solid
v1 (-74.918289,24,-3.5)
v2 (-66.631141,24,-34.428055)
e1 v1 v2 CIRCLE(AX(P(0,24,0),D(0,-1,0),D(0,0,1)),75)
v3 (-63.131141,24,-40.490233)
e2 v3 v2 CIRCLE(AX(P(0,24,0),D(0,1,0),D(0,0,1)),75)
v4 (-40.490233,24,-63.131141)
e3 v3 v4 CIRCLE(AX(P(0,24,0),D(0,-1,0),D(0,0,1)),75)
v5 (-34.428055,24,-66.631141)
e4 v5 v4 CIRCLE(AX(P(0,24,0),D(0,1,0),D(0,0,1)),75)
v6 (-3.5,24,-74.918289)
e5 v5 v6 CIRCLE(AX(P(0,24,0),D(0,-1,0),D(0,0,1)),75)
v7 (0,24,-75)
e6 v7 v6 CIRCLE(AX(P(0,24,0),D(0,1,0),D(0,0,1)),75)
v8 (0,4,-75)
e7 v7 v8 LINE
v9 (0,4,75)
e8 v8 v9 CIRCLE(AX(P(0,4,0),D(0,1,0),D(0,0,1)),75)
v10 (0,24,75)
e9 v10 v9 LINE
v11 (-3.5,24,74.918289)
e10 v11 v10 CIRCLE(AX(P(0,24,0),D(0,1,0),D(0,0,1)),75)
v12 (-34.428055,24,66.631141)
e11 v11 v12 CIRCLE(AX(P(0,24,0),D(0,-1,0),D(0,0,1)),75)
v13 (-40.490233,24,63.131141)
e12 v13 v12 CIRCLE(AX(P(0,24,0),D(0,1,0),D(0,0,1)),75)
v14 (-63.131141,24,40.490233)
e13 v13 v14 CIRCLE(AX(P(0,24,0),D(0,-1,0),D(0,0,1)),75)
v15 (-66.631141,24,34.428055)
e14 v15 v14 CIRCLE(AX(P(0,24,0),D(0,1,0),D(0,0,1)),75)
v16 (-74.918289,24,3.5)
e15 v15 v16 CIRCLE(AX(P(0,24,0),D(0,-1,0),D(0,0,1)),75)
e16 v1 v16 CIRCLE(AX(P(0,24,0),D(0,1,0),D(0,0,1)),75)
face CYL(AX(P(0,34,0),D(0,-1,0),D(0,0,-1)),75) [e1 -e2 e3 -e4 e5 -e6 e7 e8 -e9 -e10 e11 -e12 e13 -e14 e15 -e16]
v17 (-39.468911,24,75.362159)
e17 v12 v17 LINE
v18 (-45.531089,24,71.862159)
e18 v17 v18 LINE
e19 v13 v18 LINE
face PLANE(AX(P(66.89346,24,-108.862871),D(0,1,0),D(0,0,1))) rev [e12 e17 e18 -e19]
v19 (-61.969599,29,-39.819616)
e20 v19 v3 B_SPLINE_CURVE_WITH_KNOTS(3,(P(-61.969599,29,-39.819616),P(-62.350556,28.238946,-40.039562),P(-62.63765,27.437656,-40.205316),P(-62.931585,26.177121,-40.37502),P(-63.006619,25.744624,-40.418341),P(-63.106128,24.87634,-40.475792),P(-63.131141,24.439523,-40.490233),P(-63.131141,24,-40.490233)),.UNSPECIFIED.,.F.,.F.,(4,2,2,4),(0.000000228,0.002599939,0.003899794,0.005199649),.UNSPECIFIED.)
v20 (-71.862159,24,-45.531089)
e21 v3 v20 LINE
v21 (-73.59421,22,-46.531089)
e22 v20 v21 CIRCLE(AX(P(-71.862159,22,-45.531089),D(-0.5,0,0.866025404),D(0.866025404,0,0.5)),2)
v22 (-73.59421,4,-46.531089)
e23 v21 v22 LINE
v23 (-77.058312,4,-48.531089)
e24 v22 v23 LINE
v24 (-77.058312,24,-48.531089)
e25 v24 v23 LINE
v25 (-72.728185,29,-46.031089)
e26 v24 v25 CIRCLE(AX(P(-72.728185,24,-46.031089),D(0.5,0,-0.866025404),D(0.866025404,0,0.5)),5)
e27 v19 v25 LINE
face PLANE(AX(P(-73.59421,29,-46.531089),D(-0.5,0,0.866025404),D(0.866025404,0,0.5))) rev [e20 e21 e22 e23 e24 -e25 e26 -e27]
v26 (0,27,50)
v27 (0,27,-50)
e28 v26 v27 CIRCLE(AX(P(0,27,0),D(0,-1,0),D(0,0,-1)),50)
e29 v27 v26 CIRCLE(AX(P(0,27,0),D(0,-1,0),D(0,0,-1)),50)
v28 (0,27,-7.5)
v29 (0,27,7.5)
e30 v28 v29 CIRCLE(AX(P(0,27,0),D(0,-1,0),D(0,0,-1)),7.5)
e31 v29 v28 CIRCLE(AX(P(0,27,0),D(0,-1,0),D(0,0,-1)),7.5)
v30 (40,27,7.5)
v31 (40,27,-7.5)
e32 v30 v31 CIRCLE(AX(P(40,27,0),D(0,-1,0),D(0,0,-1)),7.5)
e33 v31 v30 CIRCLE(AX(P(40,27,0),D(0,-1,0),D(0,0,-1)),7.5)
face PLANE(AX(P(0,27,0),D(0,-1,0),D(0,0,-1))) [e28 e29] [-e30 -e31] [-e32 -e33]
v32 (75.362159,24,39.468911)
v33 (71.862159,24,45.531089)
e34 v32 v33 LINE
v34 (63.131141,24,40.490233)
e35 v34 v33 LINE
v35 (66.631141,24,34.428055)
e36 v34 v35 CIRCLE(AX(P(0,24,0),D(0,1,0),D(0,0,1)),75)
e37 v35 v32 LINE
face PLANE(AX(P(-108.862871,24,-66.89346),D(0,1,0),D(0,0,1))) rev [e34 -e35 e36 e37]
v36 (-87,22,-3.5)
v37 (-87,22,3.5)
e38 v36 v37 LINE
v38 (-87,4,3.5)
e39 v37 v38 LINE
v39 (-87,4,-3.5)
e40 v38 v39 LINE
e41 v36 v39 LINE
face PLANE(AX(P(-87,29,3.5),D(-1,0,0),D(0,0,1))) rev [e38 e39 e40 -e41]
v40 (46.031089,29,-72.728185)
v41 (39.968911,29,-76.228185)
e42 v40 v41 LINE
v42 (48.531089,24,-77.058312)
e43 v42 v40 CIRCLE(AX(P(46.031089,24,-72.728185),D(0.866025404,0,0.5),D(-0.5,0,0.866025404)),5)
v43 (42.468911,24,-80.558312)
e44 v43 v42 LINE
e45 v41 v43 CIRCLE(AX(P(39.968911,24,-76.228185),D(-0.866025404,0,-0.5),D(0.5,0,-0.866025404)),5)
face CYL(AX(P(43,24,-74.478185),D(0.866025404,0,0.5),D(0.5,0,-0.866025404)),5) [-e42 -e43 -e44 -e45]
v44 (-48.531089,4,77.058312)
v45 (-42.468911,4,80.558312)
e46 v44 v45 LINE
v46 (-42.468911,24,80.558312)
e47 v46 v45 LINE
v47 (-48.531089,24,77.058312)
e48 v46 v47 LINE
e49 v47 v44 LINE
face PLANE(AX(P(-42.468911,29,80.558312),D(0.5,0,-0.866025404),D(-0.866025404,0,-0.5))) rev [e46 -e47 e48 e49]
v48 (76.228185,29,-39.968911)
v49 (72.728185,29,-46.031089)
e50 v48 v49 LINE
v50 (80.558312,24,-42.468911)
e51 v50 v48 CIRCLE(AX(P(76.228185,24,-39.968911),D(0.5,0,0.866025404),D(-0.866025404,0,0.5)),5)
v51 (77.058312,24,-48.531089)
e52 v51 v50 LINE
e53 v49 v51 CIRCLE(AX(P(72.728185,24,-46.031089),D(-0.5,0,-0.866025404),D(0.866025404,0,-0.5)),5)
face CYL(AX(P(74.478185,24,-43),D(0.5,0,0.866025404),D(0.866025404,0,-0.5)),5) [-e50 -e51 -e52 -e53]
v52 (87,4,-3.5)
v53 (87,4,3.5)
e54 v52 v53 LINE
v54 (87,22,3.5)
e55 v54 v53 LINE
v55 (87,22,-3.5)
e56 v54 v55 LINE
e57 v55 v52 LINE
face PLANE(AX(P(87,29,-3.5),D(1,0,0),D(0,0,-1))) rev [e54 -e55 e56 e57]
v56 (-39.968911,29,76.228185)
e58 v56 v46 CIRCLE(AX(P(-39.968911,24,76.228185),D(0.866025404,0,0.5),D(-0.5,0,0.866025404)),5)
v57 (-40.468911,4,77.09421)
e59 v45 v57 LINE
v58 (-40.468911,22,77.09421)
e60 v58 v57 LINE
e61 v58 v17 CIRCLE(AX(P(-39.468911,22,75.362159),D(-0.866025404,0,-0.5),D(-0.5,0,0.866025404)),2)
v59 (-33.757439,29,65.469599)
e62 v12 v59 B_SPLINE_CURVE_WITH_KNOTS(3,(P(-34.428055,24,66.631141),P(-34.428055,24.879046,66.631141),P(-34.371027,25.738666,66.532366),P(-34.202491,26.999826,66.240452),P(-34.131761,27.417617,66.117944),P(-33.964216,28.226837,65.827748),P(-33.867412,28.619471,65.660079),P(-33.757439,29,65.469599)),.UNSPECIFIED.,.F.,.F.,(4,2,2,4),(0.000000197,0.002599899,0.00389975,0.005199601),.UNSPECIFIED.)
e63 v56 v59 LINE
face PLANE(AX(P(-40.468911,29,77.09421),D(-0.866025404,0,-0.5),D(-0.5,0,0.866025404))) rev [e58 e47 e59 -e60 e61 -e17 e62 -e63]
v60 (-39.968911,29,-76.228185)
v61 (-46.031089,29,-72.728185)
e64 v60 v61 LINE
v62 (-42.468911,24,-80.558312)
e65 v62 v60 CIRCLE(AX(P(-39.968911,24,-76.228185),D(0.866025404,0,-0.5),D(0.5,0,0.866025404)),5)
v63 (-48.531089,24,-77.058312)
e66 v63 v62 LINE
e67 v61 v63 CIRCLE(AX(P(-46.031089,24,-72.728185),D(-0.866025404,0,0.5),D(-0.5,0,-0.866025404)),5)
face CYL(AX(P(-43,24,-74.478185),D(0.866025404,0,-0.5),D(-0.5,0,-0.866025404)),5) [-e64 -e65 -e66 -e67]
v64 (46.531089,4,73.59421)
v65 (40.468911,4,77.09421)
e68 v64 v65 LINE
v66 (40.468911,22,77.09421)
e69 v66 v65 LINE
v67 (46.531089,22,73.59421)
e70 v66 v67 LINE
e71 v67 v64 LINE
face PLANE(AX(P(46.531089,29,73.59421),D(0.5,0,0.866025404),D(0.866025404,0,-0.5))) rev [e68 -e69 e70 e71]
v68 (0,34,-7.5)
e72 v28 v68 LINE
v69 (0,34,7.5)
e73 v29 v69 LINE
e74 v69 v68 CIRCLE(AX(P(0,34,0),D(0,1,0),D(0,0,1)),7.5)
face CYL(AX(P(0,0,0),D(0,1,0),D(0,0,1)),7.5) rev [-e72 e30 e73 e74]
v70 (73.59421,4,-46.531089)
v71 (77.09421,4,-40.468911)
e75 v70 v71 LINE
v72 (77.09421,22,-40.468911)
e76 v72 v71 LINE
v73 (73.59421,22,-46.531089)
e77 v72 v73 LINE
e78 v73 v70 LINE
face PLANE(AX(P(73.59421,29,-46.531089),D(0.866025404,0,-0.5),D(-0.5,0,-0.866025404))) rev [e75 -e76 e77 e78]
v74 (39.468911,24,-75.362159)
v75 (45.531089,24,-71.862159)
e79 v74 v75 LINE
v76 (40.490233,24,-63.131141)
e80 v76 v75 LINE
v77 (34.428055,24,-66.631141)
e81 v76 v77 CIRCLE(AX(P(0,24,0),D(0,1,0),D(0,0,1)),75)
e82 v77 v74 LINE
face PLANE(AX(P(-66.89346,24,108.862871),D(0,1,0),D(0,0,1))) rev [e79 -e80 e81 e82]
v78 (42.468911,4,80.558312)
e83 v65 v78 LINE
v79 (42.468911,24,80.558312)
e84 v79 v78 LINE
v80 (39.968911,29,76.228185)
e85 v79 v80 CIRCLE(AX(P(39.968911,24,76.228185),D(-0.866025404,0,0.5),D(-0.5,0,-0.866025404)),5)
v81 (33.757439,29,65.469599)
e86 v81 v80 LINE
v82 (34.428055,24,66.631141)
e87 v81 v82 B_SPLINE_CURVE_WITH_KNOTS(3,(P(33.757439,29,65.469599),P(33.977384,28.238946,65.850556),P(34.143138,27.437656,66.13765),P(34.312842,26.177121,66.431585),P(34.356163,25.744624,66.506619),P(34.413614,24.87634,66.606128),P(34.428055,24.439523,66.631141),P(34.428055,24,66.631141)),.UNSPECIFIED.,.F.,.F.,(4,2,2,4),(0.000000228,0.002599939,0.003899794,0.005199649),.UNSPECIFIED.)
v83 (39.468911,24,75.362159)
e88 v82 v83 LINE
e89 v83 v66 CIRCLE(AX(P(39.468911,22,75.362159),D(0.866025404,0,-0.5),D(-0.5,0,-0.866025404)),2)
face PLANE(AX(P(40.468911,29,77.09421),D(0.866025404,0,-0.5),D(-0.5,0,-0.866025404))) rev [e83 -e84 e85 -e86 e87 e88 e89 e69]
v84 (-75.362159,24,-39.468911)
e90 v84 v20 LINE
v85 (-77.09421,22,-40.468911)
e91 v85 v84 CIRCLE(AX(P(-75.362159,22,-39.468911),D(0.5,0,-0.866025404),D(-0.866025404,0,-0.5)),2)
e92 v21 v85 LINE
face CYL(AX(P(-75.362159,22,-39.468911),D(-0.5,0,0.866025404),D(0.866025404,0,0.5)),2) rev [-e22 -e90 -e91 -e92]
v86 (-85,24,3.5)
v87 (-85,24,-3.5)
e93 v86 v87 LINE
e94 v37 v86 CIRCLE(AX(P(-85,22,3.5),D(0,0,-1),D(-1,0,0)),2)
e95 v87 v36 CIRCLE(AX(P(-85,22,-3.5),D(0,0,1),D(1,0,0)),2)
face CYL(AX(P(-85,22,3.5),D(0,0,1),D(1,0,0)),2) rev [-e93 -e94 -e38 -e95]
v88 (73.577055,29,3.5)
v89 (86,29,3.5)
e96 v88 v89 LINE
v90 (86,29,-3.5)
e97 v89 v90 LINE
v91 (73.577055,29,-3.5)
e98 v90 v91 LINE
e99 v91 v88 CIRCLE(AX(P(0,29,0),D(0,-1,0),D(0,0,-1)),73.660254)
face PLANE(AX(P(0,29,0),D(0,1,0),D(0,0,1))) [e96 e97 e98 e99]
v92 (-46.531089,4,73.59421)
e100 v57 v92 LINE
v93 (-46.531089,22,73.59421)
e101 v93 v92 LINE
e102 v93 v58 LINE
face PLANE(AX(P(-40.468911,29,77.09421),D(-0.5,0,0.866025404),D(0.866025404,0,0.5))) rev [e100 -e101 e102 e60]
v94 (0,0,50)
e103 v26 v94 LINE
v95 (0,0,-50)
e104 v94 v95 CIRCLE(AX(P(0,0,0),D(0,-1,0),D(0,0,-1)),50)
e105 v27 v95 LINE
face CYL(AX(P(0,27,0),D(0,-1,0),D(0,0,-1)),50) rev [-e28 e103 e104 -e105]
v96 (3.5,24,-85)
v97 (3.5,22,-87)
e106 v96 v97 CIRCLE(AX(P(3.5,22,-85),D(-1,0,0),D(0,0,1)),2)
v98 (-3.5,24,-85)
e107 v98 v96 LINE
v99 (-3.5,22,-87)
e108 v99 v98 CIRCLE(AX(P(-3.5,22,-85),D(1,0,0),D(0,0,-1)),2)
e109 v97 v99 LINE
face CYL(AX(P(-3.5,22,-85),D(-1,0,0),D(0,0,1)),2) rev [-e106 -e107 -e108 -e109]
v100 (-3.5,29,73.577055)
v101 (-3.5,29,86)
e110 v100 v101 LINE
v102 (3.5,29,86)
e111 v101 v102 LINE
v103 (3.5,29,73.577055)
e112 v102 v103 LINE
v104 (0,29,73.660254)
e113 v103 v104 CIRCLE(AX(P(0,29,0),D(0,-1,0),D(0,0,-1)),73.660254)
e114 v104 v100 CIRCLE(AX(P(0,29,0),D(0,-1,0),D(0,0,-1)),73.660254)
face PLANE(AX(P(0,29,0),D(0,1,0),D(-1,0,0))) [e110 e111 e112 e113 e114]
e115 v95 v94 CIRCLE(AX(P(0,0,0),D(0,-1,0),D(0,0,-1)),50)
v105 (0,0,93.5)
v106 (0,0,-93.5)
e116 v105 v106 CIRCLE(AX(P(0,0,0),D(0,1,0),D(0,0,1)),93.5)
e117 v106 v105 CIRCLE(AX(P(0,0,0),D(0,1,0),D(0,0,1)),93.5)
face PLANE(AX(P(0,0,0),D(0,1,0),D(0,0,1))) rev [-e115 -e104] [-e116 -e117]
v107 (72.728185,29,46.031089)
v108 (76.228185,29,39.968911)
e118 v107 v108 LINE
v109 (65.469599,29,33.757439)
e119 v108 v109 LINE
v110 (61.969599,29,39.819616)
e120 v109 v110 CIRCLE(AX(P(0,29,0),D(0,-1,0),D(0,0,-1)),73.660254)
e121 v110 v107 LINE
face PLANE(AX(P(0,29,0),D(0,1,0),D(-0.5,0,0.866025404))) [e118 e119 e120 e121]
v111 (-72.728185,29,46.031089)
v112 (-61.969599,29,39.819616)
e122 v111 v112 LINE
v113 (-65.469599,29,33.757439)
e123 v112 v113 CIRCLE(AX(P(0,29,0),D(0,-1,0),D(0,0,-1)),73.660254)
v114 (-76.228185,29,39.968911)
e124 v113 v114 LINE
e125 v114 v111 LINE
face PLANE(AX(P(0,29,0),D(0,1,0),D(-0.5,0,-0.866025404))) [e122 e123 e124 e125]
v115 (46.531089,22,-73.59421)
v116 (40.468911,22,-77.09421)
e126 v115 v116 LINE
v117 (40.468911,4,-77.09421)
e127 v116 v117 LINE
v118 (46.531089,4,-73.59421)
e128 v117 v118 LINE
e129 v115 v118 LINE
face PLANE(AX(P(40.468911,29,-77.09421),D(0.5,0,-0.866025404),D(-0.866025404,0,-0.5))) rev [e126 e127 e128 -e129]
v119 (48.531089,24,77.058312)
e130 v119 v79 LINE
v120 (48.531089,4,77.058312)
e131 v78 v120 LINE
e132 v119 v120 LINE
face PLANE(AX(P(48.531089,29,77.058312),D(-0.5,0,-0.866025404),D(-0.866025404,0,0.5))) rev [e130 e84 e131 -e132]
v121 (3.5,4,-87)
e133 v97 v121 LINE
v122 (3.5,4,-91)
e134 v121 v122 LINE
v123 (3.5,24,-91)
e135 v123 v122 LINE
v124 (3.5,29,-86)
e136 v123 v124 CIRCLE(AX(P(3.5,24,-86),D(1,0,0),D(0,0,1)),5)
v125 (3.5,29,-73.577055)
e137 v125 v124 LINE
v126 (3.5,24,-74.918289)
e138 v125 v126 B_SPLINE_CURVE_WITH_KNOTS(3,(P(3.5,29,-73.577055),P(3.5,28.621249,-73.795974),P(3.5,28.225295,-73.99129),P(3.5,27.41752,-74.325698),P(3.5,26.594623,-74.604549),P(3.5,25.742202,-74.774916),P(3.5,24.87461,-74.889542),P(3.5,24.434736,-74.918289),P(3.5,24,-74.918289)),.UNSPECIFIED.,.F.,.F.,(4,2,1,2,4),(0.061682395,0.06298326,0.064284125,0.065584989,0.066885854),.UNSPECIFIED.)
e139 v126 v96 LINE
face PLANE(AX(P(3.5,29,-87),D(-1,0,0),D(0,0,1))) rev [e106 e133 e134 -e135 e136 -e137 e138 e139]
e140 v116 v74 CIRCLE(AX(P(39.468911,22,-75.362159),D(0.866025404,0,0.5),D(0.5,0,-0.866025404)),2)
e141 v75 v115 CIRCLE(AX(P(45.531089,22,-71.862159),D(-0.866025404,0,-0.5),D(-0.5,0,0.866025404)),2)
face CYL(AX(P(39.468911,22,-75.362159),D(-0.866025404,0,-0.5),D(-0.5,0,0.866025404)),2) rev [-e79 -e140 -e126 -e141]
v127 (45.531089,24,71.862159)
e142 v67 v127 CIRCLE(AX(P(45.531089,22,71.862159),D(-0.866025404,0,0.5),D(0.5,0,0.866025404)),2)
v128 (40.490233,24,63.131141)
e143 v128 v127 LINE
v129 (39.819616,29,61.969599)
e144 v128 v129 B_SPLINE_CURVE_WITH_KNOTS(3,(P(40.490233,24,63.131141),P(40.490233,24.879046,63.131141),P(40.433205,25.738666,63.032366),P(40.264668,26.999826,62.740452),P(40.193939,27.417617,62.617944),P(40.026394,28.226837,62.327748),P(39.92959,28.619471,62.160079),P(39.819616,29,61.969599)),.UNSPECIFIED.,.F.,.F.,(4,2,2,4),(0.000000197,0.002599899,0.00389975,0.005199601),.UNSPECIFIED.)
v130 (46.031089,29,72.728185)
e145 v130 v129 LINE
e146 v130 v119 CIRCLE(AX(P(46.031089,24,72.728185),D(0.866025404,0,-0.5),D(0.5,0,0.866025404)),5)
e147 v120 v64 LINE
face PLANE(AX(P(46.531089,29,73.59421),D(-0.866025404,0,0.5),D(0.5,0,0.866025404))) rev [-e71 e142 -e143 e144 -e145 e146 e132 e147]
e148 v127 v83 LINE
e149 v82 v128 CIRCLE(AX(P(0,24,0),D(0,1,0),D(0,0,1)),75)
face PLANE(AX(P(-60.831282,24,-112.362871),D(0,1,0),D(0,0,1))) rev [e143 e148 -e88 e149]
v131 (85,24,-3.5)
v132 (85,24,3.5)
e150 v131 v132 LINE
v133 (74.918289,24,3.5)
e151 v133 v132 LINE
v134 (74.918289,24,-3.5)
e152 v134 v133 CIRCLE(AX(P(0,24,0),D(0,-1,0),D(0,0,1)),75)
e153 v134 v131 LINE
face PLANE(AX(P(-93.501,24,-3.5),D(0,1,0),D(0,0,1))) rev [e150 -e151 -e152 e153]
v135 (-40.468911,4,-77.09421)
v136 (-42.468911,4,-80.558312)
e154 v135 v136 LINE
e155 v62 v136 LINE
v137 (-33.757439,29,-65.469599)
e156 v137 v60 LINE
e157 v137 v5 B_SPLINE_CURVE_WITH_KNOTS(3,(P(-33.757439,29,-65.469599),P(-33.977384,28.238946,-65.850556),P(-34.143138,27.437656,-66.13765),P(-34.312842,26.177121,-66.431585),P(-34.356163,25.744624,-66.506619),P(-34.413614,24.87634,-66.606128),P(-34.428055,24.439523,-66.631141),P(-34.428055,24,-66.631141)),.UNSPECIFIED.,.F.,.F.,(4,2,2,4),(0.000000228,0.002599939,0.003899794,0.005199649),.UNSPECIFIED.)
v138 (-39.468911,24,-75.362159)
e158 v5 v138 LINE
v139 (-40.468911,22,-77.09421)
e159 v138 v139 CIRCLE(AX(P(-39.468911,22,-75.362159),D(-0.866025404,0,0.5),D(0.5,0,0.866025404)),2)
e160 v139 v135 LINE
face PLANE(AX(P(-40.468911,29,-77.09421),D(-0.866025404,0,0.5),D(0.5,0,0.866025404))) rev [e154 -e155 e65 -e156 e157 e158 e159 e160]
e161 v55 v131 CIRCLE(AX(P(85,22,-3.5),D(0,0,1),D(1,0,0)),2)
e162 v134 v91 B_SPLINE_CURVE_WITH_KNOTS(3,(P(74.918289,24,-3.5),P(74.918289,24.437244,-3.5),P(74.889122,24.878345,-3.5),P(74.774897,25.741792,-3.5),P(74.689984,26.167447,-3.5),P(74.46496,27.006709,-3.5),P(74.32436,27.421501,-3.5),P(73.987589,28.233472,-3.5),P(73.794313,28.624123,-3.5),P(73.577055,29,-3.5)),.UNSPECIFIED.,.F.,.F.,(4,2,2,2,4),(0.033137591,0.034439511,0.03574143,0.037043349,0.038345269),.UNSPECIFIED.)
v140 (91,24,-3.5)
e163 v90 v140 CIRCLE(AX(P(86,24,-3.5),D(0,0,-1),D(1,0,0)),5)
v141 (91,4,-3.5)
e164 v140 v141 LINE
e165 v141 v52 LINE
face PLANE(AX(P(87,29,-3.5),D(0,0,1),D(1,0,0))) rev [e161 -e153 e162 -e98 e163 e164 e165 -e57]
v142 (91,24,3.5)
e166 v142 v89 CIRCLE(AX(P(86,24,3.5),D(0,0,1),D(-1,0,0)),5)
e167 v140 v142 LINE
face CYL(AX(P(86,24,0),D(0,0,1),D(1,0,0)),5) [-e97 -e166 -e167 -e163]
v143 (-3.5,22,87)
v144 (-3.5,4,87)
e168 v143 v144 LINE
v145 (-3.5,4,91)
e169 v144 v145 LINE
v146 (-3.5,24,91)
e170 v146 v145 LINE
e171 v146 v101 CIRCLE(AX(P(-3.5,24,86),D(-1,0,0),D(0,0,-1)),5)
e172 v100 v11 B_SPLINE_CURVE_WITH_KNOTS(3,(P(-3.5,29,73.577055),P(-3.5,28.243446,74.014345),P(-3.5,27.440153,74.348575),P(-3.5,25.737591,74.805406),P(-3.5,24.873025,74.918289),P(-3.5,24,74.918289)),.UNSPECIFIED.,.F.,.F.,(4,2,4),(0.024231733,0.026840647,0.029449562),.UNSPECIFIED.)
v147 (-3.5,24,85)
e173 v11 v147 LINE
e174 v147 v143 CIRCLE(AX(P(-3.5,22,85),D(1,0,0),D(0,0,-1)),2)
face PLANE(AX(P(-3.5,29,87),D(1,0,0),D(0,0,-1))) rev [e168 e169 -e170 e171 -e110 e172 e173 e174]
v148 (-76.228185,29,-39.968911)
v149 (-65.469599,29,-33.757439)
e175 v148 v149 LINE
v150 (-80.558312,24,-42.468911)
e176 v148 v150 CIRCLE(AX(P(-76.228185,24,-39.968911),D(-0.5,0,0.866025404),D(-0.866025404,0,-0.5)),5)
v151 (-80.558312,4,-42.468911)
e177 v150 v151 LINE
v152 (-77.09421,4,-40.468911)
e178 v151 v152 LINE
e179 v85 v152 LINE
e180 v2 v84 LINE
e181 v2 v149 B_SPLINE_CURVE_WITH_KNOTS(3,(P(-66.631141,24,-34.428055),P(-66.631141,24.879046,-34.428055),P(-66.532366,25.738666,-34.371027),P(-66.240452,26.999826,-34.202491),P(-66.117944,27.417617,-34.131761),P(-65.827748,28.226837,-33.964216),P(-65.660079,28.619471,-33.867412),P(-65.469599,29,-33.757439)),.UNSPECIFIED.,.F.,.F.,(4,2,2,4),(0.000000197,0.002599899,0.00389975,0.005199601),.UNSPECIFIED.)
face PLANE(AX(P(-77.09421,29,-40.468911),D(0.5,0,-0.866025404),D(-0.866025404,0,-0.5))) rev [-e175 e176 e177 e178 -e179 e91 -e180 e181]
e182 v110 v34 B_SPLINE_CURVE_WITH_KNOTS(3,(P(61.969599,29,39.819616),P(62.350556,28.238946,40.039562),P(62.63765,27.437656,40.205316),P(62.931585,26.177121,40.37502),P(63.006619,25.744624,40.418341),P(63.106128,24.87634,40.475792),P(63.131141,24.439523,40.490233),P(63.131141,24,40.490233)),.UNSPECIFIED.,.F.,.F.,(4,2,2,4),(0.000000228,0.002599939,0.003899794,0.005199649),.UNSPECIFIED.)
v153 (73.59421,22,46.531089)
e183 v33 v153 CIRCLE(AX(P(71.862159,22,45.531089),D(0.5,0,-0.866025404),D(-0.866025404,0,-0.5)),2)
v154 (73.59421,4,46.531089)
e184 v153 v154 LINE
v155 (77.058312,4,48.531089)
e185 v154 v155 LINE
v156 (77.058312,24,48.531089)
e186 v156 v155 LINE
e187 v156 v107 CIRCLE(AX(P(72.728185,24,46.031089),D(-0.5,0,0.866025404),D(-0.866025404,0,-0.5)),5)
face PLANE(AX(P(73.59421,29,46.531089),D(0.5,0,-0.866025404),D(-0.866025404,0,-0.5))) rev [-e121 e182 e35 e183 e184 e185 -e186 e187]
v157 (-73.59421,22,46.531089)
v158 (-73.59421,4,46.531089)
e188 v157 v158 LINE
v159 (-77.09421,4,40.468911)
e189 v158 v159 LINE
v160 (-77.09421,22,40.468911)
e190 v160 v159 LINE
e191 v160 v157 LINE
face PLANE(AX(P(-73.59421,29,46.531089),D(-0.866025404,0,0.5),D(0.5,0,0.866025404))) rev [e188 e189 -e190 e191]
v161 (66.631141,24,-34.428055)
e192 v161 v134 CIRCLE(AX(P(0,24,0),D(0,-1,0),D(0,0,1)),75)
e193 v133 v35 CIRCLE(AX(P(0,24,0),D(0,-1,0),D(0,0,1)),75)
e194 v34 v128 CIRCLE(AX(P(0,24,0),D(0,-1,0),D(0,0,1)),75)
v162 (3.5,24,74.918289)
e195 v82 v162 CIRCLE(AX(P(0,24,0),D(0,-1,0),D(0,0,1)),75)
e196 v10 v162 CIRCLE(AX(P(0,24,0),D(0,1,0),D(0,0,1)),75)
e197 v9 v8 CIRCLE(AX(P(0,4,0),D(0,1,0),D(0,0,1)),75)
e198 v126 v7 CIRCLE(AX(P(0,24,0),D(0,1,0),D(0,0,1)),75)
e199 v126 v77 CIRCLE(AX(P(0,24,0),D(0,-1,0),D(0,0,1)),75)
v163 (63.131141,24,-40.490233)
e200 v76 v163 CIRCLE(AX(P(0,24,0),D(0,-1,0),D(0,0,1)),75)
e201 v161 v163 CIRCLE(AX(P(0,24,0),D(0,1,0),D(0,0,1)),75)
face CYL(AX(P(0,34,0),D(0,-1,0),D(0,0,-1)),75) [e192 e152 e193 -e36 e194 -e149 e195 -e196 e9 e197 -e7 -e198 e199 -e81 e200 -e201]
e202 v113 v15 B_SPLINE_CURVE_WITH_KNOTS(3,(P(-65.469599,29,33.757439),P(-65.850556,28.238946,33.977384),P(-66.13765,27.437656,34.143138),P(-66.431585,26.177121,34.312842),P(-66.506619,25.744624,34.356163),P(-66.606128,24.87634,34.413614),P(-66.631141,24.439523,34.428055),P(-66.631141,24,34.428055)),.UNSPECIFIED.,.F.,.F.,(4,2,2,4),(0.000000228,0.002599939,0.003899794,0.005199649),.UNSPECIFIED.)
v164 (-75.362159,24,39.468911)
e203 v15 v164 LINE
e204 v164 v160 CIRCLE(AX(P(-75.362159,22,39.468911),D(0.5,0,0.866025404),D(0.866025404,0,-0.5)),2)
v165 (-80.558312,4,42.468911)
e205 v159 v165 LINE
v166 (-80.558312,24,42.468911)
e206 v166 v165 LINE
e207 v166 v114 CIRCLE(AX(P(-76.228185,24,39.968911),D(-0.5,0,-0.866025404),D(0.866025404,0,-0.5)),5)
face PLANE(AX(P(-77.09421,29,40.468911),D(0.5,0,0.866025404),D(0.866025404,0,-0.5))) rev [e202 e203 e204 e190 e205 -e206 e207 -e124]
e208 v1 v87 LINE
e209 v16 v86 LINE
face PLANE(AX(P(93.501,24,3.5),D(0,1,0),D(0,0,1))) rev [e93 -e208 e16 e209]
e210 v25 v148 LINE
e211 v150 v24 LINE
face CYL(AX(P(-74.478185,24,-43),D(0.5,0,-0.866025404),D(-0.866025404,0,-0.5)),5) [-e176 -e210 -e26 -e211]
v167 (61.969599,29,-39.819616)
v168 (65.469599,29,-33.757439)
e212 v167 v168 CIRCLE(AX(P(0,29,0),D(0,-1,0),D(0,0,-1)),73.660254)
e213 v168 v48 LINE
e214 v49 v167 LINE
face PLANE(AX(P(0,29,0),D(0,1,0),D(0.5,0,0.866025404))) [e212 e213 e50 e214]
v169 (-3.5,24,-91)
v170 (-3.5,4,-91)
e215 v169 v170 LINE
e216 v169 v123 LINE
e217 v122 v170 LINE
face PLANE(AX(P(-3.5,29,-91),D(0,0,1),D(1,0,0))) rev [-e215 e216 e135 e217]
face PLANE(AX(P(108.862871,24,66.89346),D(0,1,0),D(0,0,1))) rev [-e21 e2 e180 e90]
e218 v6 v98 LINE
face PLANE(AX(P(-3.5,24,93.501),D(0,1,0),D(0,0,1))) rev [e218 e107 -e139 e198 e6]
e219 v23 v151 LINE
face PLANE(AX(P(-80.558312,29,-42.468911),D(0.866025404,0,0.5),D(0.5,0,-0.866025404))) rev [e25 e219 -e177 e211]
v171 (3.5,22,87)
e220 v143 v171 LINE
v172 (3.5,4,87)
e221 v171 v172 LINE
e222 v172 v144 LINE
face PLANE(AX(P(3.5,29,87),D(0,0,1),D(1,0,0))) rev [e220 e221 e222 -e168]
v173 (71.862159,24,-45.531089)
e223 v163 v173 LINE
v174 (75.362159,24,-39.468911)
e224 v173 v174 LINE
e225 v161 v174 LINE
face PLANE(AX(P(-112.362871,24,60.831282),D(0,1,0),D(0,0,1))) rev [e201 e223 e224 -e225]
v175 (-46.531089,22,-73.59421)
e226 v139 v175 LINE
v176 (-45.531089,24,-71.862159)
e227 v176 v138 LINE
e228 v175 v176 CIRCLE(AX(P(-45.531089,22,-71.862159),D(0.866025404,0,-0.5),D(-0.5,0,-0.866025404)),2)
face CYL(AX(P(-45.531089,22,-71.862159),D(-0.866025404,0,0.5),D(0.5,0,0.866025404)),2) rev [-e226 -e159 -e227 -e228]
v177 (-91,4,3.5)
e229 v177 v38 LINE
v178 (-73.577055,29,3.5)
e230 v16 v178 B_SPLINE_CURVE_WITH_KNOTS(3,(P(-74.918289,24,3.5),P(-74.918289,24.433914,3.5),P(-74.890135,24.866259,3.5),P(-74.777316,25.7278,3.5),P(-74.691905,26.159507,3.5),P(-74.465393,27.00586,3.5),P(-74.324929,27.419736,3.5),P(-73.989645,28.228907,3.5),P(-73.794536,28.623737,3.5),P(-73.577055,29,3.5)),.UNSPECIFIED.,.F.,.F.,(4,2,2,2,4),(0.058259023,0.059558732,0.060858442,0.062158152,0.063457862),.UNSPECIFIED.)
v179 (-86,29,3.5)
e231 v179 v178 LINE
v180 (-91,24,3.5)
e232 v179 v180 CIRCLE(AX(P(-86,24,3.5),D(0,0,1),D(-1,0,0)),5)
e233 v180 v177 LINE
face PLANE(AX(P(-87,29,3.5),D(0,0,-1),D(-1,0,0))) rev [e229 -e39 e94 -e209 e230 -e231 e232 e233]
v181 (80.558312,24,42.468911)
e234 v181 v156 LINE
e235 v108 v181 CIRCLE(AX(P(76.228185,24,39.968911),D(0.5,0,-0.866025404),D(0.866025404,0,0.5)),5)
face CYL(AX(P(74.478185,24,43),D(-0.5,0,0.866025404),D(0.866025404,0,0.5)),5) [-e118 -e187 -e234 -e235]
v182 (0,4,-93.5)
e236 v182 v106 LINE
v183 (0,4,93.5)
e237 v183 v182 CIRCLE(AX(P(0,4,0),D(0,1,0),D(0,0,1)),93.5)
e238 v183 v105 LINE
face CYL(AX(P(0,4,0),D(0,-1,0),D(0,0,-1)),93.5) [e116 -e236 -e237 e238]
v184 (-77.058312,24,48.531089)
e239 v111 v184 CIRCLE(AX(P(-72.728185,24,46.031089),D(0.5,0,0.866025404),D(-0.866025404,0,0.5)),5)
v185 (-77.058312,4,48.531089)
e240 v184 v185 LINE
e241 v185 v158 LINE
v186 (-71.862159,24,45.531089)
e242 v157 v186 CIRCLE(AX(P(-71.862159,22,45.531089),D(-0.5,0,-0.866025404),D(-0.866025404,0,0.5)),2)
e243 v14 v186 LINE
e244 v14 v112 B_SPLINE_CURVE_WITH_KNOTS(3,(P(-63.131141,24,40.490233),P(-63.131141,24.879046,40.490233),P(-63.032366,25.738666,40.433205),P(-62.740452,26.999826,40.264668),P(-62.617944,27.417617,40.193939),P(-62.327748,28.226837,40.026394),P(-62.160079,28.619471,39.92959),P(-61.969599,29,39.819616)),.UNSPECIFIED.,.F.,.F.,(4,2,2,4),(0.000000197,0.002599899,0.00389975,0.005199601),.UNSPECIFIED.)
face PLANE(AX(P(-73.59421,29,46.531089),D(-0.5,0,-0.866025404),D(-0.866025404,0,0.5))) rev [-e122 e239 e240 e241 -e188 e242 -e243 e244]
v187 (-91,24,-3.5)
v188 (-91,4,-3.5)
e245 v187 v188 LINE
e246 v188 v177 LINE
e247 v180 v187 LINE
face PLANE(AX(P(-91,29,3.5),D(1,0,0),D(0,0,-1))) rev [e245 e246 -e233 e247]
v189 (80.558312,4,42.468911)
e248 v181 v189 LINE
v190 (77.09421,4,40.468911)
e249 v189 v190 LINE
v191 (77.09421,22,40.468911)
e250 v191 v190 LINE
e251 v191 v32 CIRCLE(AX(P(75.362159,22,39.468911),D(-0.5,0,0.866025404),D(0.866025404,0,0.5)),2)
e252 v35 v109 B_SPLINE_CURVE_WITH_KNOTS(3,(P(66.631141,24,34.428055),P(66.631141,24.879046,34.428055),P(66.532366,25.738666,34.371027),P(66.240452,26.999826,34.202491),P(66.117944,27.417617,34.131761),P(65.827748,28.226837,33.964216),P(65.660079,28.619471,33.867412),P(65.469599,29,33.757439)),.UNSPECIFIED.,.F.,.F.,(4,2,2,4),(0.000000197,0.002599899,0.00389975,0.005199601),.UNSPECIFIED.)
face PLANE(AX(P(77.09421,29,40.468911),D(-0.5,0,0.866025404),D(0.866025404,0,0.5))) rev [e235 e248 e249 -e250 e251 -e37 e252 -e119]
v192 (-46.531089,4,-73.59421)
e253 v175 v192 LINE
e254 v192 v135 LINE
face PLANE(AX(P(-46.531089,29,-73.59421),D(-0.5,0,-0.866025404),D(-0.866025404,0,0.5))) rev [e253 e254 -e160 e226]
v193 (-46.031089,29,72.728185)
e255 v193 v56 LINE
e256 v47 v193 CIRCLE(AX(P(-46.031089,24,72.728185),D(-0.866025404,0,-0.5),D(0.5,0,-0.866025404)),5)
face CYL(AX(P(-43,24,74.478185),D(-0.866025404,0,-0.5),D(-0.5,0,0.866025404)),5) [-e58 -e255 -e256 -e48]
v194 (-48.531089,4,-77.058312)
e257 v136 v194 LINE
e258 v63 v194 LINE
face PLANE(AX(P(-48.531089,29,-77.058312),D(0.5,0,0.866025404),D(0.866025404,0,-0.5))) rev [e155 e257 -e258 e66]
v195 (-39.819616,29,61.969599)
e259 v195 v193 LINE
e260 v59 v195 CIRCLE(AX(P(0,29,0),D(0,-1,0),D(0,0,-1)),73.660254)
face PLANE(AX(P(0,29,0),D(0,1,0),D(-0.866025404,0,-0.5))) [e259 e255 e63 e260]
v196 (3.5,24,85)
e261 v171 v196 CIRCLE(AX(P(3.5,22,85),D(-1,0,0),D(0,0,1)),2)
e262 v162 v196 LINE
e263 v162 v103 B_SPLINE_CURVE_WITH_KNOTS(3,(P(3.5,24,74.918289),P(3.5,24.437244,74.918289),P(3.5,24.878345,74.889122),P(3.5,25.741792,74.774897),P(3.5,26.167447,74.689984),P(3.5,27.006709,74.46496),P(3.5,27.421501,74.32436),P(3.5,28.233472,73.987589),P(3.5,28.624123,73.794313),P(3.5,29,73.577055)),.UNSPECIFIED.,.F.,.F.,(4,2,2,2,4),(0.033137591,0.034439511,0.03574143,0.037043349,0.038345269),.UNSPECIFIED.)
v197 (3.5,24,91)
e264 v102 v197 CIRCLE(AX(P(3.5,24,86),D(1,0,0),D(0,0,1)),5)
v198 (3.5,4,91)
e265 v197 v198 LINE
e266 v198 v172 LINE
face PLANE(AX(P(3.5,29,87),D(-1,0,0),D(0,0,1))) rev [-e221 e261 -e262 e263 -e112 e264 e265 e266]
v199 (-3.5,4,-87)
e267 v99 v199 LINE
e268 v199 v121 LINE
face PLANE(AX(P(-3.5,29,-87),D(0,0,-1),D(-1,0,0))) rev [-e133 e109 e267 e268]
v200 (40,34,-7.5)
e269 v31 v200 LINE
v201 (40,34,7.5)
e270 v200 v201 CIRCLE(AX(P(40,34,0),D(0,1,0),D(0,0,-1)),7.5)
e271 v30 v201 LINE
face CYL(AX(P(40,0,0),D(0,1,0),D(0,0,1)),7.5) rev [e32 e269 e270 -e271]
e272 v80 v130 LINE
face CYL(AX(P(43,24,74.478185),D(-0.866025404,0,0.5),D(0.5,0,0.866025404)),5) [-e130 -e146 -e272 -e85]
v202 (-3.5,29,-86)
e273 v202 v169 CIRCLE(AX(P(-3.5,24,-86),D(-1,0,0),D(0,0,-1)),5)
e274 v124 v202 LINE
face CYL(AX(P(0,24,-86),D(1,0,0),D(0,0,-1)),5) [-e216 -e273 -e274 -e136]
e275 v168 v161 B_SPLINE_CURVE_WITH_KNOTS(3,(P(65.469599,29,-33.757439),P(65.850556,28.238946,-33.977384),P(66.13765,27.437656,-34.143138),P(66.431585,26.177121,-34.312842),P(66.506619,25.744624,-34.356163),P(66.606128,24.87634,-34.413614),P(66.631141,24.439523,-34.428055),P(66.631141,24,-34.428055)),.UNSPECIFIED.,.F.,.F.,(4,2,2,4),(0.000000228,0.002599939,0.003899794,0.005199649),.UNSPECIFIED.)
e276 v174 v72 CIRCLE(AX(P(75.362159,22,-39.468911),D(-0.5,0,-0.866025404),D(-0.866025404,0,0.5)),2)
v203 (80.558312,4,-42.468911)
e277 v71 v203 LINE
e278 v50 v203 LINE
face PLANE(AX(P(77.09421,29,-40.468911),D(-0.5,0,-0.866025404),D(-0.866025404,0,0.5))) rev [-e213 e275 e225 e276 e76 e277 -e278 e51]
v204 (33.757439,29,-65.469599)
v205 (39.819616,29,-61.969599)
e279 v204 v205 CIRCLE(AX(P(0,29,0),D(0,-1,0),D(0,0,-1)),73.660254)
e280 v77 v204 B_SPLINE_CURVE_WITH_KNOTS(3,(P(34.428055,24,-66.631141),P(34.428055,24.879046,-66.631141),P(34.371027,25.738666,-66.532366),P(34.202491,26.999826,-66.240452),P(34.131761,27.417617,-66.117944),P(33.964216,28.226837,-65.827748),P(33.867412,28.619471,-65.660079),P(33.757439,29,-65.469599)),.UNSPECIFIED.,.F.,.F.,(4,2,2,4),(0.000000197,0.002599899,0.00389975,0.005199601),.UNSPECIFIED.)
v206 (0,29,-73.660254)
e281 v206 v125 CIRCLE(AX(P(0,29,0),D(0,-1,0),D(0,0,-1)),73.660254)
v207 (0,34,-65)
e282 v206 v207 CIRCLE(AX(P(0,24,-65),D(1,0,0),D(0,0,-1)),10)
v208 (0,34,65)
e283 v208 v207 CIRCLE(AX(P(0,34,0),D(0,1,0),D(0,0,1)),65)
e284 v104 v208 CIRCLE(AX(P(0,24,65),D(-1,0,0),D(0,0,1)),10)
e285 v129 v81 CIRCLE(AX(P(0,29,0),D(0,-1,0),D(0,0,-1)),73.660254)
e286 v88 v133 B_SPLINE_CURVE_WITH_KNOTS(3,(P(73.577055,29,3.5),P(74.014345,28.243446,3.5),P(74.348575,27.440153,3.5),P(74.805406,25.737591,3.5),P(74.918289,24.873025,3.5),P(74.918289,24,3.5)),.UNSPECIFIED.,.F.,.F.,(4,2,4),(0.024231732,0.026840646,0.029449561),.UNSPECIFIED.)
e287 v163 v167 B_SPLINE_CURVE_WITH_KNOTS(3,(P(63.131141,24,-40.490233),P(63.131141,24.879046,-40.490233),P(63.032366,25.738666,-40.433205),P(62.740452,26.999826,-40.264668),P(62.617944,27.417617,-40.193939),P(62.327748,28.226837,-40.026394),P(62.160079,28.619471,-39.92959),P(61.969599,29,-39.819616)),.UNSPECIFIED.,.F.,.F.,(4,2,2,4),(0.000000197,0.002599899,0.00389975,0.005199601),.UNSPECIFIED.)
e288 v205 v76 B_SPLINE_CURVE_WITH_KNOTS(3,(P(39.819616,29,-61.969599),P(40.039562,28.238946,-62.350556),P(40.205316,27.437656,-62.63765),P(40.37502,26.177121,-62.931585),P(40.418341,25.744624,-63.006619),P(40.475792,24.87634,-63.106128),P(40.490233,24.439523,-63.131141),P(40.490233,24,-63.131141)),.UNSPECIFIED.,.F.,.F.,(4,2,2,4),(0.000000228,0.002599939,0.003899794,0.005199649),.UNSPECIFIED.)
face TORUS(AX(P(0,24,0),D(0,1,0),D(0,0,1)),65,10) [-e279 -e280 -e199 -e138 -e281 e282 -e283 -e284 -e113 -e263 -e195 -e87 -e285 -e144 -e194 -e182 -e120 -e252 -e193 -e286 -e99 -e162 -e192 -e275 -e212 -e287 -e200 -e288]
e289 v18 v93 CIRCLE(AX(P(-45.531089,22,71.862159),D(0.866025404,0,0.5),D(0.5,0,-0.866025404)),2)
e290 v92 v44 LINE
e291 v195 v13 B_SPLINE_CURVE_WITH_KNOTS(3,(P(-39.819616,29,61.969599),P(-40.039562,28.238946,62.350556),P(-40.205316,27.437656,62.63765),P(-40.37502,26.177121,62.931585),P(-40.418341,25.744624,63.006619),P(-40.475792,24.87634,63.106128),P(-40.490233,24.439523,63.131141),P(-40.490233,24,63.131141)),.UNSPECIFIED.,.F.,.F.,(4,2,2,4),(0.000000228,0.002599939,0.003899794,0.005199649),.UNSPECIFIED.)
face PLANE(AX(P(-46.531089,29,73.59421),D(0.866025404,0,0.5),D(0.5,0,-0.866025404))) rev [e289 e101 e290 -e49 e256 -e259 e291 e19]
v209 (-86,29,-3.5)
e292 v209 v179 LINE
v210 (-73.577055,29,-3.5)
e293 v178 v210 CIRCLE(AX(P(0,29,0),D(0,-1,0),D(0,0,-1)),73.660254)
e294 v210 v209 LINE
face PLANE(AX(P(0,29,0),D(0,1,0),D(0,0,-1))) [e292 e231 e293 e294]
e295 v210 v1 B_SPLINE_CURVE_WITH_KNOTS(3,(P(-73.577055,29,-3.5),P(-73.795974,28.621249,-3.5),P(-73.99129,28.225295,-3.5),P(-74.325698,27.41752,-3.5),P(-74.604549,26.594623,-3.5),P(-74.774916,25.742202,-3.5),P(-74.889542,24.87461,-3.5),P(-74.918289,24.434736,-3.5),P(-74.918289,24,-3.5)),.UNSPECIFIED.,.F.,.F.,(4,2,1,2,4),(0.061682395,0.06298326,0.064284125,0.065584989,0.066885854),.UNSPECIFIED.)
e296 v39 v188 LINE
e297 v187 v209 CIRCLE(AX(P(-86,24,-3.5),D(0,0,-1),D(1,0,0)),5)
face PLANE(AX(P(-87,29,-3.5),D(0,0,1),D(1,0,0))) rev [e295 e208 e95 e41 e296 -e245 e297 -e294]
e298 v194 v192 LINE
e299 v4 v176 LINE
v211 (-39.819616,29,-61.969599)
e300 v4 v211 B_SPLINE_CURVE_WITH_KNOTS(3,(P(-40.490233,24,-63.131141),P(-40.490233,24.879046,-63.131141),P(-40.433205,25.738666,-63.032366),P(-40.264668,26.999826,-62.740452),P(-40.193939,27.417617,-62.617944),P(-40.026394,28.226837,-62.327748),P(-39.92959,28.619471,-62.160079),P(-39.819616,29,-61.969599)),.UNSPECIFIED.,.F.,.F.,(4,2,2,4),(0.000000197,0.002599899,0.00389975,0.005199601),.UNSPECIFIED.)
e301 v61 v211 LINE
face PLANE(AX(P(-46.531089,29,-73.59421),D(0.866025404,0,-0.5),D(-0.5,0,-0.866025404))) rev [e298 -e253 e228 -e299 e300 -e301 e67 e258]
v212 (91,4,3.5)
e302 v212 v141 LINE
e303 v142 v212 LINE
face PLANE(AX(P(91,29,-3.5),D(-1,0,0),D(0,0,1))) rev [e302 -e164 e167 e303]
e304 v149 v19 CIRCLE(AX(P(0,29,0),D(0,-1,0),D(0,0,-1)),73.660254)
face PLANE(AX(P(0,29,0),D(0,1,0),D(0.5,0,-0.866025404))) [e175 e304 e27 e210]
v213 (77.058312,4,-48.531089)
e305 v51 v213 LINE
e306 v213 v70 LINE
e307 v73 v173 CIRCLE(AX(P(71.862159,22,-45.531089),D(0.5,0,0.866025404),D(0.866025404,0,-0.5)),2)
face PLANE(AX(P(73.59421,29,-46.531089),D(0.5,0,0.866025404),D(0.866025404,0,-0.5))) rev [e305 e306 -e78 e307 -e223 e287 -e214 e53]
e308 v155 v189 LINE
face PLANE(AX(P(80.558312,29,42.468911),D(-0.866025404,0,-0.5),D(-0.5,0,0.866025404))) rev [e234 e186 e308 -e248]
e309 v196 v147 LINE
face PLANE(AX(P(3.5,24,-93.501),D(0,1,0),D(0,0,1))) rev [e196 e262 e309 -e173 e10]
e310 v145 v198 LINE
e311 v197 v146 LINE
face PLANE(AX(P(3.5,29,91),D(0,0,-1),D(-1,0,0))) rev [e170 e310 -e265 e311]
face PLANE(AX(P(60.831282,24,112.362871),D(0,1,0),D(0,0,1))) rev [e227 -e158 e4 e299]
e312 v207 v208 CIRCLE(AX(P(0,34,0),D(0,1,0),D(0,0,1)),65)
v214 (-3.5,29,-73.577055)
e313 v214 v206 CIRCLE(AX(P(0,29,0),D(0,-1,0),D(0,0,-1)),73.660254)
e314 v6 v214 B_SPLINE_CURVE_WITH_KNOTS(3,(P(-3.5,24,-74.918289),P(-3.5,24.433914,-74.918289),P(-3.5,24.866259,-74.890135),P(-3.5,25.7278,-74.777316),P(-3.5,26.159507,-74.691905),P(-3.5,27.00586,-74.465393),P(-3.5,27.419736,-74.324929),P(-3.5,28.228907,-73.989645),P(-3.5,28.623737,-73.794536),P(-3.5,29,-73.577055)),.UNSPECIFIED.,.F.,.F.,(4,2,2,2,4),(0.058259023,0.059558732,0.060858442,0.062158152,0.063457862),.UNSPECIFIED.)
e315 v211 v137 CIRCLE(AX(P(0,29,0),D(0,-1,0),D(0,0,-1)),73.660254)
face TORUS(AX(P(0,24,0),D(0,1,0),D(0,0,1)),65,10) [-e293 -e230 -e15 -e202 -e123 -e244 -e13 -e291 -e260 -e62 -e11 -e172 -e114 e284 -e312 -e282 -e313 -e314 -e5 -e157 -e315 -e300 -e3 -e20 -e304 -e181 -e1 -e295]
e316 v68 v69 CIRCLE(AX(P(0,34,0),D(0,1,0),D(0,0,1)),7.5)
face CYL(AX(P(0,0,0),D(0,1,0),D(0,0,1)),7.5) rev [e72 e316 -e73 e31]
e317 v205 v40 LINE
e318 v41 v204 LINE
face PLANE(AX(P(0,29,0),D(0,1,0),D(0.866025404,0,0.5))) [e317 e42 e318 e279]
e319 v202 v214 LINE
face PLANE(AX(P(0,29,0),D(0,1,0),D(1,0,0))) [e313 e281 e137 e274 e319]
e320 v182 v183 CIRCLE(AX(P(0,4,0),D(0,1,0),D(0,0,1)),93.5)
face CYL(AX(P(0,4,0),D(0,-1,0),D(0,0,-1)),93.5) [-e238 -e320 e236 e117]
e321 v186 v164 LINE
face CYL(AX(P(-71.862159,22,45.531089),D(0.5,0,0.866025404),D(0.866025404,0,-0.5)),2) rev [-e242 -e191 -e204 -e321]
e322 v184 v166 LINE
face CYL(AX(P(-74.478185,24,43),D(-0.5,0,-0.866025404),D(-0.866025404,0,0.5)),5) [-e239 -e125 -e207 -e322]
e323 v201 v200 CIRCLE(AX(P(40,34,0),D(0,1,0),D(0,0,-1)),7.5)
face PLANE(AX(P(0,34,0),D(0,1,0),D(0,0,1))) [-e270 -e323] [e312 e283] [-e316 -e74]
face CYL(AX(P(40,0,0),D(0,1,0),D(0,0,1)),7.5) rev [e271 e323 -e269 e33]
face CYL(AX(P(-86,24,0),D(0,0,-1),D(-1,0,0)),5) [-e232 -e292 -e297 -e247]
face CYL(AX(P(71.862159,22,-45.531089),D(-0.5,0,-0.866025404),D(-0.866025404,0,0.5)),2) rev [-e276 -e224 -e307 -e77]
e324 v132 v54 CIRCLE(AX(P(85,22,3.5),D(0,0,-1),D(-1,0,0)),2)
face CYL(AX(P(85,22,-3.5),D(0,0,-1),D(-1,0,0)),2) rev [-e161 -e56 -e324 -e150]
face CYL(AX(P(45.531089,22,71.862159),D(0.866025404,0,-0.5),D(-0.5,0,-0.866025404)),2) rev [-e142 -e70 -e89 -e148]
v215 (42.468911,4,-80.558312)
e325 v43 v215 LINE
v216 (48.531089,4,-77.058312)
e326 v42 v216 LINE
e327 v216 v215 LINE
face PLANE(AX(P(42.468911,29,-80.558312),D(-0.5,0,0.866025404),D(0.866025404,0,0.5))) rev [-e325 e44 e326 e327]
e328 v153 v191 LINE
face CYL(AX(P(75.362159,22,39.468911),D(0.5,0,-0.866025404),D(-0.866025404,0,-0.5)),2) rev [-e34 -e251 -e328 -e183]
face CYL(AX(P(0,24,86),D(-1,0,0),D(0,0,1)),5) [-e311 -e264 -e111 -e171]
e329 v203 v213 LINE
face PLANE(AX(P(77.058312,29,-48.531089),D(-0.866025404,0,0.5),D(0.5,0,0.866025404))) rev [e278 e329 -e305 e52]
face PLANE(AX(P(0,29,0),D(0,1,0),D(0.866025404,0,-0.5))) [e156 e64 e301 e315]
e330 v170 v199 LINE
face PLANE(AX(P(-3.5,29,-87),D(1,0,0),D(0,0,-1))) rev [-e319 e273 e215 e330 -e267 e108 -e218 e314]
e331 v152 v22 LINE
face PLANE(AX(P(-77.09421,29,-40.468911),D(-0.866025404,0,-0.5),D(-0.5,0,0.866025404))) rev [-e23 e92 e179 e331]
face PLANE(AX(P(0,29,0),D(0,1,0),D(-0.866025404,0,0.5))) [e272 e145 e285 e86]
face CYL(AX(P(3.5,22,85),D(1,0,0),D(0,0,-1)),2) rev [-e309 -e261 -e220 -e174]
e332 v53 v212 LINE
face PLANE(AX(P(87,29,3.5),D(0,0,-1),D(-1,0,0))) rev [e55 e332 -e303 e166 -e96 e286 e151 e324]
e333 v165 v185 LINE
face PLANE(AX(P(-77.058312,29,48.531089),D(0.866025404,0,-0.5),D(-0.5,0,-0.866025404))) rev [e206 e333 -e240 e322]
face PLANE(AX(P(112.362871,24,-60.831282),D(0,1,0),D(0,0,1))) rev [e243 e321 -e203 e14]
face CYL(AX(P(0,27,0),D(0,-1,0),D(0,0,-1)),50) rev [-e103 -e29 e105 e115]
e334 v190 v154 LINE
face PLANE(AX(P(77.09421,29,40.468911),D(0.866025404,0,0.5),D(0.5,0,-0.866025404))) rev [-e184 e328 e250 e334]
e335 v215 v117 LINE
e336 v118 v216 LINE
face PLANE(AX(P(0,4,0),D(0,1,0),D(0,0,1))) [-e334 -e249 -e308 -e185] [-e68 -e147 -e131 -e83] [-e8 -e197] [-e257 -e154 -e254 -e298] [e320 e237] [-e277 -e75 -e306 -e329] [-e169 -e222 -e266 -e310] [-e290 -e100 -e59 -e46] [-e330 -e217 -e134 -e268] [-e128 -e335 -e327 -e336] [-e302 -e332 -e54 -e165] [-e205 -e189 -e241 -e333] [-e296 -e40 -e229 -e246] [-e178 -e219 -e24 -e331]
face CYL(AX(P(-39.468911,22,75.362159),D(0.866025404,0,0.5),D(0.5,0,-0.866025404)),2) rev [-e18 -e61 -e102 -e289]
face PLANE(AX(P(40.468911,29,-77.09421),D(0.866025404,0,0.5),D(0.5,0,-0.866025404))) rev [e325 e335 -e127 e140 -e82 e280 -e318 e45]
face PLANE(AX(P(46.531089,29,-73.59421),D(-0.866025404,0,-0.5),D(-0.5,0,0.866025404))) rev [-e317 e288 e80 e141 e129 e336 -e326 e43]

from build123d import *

# Parameters (mm, degrees)
SKETCH1_R                = 75
BOSS_EXTRUDE1_DEPTH      = 34
SKETCH3_R                = 93.5
BOSS_EXTRUDE2_DEPTH      = 4
FILLET1_R                = 10
SKETCH4_R                = 50
CUT_EXTRUDE1_DEPTH       = 27
SKETCH6_W                = 4
SKETCH6_H                = 7
BOSS_EXTRUDE3_DEPTH      = 25
BOSS_EXTRUDE4_REACH      = 208.103
SKETCH7_W                = 7
SKETCH7_H                = 5
FILLET2_R                = 5
FILLET3_R                = 2
CIRPATTERN2_COUNT        = 12
FILLET2_OF_CIRPATTERN2_R = 5
FILLET3_OF_CIRPATTERN2_R = 2
SKETCH8_R                = 7.5
CUT_EXTRUDE2_DEPTH       = 137.530216436


with BuildPart() as part:
    # Sketch1 → Boss-Extrude1 (new body)
    with BuildSketch(Plane(origin=(0, 0, 0), x_dir=(1, 0, 0), z_dir=(0, 1, 0))):
        with Locations(Location((0, 0, 0), (0, 0, 270))):
            Circle(SKETCH1_R)
    extrude(amount=BOSS_EXTRUDE1_DEPTH)

    # Sketch3 → Boss-Extrude2 (add)
    with BuildSketch(Plane(origin=(0, 0, 0), x_dir=(1, 0, 0), z_dir=(0, 1, 0))):
        with Locations(Location((0, 0, 0), (0, 0, 270))):
            Circle(SKETCH3_R)
    extrude(amount=BOSS_EXTRUDE2_DEPTH)

    # Fillet1
    fillet1_edges = [part.edges().sort_by_distance(p)[0] for p in [
        (0, 34, -75),
    ]]
    fillet(fillet1_edges, radius=FILLET1_R)

    # Sketch4 → Cut-Extrude1 (cut)
    with BuildSketch(Plane.XZ):
        with Locations(Location((0, 0, 0), (0, 0, 270))):
            Circle(SKETCH4_R)
    extrude(amount=-CUT_EXTRUDE1_DEPTH, mode=Mode.SUBTRACT)

    # Sketch6 → Boss-Extrude3 (add)
    with BuildSketch(Plane(origin=(0, 4, 0), x_dir=(1, 0, 0), z_dir=(0, 1, 0))):
        with Locations((89, 0)):
            Rectangle(SKETCH6_W, SKETCH6_H)
    boss_extrude3 = extrude(amount=BOSS_EXTRUDE3_DEPTH)

    # Sketch7 → Boss-Extrude4 (add, up to next)
    with BuildSketch(Plane.ZY.offset(-87), mode=Mode.PRIVATE) as boss_extrude4_sk1:
        with Locations((0, 26.5)):
            Rectangle(SKETCH7_W, SKETCH7_H)
    boss_extrude4_tool1 = extrude(boss_extrude4_sk1.sketch, amount=BOSS_EXTRUDE4_REACH, mode=Mode.PRIVATE) - part.part
    boss_extrude4 = boss_extrude4_tool1.solids().sort_by_distance((87, 26.5, 0))[0]
    add(boss_extrude4)

    # Fillet2
    fillet2_edges = [part.edges().sort_by_distance(p)[0] for p in [
        (91, 29, 0),
    ]]
    fillet(fillet2_edges, radius=FILLET2_R)

    # Fillet3
    fillet3_edges = [part.edges().sort_by_distance(p)[0] for p in [
        (87, 24, 0),
    ]]
    fillet(fillet3_edges, radius=FILLET3_R)

    # CirPattern2: Boss-Extrude3, Boss-Extrude4 ×12 about axis
    cirpattern2_axis = Axis((0, 0, 0), (0, 1, 0))
    add([boss_extrude3.rotate(cirpattern2_axis, i * 360 / CIRPATTERN2_COUNT) for i in range(1, CIRPATTERN2_COUNT)])
    add([boss_extrude4.rotate(cirpattern2_axis, i * 360 / CIRPATTERN2_COUNT) for i in range(1, CIRPATTERN2_COUNT)])

    # Fillet2 of CirPattern2
    fillet2_of_cirpattern2_edges = [part.edges().sort_by_distance(p)[0] for p in [
        (78.808311744, 29, -45.5),
        (45.5, 29, -78.808311744),
        (0, 29, -91),
        (-45.5, 29, -78.808311744),
        (-78.808311744, 29, -45.5),
        (-91, 29, 0),
        (-78.808311744, 29, 45.5),
        (-45.5, 29, 78.808311744),
        (0, 29, 91),
        (45.5, 29, 78.808311744),
        (78.808311744, 29, 45.5),
    ]]
    fillet(fillet2_of_cirpattern2_edges, radius=FILLET2_OF_CIRPATTERN2_R)

    # Fillet3 of CirPattern2
    fillet3_of_cirpattern2_edges = [part.edges().sort_by_distance(p)[0] for p in [
        (75.344210129, 24, -43.5),
        (43.5, 24, -75.344210129),
        (0, 24, -87),
        (-43.5, 24, -75.344210129),
        (-75.344210129, 24, -43.5),
        (-87, 24, 0),
        (-75.344210129, 24, 43.5),
        (-43.5, 24, 75.344210129),
        (0, 24, 87),
        (43.5, 24, 75.344210129),
        (75.344210129, 24, 43.5),
    ]]
    fillet(fillet3_of_cirpattern2_edges, radius=FILLET3_OF_CIRPATTERN2_R)

    # Sketch8 → Cut-Extrude2 (cut, through all)
    with BuildSketch(Plane(origin=(0, 34, 0), x_dir=(1, 0, 0), z_dir=(0, 1, 0))):
        with Locations(Location((0, 0, 0), (0, 0, 270))):
            Circle(SKETCH8_R)
        with Locations(Location((40, 0, 0), (0, 0, 90))):
            Circle(SKETCH8_R)
    extrude(amount=-CUT_EXTRUDE2_DEPTH, mode=Mode.SUBTRACT)


solid = part.part
